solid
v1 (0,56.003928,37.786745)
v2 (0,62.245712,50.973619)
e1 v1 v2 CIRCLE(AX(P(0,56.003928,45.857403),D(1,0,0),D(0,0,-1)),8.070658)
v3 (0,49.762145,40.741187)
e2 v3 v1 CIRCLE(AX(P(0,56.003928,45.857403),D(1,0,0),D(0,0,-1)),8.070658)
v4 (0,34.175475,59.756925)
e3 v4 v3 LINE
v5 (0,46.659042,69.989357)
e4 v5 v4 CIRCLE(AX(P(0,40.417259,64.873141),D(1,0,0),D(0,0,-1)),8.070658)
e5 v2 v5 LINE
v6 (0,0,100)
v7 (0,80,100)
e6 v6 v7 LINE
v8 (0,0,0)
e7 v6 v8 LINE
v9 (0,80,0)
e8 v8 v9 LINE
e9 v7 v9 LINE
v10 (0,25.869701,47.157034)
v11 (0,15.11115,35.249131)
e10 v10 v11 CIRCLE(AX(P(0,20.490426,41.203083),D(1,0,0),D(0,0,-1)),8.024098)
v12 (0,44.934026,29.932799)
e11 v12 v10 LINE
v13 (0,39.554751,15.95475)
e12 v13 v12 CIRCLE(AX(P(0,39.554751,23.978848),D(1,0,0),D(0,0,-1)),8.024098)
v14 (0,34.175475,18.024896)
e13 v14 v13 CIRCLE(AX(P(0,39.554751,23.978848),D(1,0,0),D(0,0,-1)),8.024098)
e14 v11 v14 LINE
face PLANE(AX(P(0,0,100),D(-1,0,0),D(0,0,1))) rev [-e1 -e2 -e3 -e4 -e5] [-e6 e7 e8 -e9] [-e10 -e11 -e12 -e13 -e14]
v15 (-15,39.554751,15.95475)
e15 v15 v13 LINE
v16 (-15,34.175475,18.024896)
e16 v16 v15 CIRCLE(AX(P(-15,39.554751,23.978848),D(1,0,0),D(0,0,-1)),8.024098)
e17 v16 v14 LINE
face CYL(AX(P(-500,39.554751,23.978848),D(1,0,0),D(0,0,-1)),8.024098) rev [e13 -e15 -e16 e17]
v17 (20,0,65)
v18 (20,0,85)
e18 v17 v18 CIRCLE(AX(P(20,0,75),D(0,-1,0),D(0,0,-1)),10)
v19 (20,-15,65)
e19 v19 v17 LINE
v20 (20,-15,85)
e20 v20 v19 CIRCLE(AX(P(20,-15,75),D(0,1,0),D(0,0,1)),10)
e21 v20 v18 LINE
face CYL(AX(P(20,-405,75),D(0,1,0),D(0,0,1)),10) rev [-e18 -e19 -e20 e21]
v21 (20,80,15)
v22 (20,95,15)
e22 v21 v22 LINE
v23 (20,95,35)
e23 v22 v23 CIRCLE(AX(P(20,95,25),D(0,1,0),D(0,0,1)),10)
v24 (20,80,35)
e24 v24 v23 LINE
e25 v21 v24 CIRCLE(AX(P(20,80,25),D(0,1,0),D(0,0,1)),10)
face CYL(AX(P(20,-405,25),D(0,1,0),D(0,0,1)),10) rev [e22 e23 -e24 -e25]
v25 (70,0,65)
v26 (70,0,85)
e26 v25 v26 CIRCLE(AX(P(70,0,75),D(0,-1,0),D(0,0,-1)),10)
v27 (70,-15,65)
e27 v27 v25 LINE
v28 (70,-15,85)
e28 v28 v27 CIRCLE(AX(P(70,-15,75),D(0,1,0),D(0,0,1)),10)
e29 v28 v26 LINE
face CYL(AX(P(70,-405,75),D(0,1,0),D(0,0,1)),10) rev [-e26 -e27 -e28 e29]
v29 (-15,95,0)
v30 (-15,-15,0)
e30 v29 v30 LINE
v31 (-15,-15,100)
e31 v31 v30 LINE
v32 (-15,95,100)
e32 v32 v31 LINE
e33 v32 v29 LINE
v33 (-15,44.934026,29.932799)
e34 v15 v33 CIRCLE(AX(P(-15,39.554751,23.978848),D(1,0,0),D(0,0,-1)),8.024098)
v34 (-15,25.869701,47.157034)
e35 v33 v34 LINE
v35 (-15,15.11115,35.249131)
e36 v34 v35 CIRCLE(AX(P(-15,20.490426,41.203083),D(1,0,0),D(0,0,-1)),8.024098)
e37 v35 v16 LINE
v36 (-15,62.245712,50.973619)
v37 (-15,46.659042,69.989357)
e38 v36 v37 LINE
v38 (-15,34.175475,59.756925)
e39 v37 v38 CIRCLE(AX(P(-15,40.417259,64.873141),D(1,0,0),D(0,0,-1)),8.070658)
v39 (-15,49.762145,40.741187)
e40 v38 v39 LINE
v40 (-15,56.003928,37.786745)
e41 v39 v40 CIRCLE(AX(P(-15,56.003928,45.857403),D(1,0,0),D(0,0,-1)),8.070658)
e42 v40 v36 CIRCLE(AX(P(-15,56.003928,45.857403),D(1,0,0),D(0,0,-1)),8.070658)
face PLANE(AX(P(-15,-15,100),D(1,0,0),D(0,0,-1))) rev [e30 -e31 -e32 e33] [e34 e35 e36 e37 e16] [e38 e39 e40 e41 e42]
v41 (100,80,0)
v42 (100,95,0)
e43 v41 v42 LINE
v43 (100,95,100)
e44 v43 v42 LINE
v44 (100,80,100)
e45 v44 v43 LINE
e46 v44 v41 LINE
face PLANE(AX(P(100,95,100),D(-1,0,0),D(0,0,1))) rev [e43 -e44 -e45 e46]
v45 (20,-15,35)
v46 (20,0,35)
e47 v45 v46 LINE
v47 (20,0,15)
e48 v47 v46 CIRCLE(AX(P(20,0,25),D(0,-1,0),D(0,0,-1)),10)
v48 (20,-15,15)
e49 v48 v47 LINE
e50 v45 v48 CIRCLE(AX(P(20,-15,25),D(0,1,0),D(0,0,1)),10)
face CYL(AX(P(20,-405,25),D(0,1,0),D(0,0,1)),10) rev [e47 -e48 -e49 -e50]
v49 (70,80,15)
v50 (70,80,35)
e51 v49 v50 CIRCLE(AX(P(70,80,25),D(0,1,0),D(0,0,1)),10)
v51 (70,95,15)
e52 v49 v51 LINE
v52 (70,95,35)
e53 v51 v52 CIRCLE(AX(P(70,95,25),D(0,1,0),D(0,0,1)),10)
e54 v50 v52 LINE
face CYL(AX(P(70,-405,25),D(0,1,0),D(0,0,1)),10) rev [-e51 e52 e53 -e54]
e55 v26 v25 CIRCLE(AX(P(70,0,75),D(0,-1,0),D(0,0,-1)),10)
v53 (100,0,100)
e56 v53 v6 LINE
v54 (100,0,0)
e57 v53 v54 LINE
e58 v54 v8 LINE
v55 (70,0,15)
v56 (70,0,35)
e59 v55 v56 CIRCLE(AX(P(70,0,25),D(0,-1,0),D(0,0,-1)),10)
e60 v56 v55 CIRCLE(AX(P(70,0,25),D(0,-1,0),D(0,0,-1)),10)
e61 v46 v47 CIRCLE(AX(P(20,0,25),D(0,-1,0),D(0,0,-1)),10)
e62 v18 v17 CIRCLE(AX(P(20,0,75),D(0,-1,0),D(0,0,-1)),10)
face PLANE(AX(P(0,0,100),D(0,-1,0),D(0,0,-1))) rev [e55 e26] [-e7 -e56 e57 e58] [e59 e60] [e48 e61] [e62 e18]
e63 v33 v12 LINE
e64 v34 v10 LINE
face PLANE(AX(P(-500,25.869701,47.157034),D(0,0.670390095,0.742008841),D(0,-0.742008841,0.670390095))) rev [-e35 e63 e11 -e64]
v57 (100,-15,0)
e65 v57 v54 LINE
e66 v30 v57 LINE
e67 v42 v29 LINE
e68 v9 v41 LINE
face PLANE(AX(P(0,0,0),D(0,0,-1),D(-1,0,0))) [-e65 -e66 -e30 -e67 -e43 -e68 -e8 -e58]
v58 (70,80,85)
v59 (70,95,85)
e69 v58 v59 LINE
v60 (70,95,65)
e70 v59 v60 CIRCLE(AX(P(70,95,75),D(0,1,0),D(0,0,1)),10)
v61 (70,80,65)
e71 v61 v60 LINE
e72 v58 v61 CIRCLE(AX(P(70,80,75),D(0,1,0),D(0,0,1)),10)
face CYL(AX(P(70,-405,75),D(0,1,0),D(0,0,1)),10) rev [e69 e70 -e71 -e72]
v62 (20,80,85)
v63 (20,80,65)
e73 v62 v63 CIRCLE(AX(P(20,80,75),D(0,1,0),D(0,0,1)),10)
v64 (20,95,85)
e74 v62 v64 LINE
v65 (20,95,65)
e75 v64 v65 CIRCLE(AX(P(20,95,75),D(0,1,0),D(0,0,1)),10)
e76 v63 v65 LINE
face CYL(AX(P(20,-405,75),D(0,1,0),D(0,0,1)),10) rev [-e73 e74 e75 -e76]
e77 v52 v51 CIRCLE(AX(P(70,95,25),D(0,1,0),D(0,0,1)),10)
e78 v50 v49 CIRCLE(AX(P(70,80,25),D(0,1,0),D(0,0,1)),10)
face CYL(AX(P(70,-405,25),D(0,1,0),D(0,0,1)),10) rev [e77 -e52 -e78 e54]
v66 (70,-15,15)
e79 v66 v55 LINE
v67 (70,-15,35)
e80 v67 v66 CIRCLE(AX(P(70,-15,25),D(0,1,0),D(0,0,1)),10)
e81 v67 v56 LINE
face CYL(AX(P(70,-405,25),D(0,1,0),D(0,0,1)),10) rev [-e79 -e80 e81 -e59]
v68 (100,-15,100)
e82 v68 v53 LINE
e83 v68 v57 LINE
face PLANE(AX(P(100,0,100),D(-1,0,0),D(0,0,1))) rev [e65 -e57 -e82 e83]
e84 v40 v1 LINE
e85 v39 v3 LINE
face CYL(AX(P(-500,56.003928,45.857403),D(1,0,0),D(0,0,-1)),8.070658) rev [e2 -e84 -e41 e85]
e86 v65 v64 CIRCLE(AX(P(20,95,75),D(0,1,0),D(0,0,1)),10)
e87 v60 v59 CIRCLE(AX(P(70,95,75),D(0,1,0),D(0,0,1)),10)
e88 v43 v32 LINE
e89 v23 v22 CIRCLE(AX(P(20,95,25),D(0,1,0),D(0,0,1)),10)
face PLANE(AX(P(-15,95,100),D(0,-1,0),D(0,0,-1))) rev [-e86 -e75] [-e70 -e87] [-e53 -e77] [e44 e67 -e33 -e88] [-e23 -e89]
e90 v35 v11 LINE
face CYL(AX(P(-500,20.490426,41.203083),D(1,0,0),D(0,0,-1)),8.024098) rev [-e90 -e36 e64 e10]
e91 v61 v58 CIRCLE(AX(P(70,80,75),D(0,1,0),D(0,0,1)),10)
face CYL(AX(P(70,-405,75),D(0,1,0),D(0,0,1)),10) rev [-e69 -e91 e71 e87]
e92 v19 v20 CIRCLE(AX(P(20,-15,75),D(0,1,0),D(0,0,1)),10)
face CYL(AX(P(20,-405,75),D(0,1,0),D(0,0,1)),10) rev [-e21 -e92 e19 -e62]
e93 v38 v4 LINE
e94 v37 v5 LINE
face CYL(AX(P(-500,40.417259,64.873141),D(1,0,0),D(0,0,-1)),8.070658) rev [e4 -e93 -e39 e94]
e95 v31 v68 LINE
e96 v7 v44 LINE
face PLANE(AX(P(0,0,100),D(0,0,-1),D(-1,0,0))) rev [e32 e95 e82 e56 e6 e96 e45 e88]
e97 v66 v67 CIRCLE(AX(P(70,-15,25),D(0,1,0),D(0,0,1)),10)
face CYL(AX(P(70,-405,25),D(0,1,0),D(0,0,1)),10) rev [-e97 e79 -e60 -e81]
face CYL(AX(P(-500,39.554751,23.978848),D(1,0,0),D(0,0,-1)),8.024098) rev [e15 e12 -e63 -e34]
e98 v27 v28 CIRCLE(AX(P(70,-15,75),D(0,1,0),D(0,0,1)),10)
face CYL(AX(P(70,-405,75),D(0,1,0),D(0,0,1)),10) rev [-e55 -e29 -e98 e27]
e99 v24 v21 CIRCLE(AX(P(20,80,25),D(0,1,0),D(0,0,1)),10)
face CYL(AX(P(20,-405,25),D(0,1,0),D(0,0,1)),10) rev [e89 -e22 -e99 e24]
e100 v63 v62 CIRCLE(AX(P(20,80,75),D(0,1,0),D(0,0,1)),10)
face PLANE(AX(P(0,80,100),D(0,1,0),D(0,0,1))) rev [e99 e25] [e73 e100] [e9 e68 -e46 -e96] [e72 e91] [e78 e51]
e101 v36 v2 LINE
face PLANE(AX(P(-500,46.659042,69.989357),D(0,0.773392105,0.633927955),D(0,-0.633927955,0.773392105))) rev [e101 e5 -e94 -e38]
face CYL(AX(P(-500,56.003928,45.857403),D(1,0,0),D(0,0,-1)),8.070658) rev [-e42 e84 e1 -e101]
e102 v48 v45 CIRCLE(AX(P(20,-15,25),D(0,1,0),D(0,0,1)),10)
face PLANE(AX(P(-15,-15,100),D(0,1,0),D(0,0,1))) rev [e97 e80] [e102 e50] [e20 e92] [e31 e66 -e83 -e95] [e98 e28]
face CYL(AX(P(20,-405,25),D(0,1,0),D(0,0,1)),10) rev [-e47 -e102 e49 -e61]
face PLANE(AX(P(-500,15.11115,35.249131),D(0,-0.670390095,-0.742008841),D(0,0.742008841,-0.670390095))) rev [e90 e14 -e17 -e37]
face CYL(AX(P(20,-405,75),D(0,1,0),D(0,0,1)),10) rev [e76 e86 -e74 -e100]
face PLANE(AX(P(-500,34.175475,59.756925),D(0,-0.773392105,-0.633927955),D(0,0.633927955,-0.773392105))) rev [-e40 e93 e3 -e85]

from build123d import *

# Parameters (mm, degrees)
BOSS_EXTRUDE1_DEPTH = 100
SKETCH2_R           = 10
CUT_EXTRUDE1_DEPTH  = 500
CUT_EXTRUDE2_DEPTH  = 500


with BuildPart() as part:
    # Sketch1 → Boss-Extrude1 (new body)
    with BuildSketch(Plane.XY):
        Polygon((0, 0), (100, 0), (100, -15), (-15, -15), (-15, 95), (100, 95), (100, 80), (0, 80), align=None)
    extrude(amount=BOSS_EXTRUDE1_DEPTH)

    # Sketch2 → Cut-Extrude1 (cut)
    with BuildSketch(Plane(origin=(0, 95, 0), x_dir=(1, 0, 0), z_dir=(0, 1, 0))):
        with Locations(Location((20, -25, 0), (0, 0, 270))):
            Circle(SKETCH2_R)
        with Locations(Location((70, -25, 0), (0, 0, 270))):
            Circle(SKETCH2_R)
        with Locations(Location((20, -75, 0), (0, 0, 270))):
            Circle(SKETCH2_R)
        with Locations(Location((70, -75, 0), (0, 0, 270))):
            Circle(SKETCH2_R)
    extrude(amount=-CUT_EXTRUDE1_DEPTH, mode=Mode.SUBTRACT)

    # Sketch3 → Cut-Extrude2 (cut)
    with BuildSketch(Plane(origin=(0, 0, 0), x_dir=(0, 0, -1), z_dir=(1, 0, 0))):
        with BuildLine():
            Line((-69.989356501, 46.65904216), (-50.973619408, 62.245711909))
            ThreePointArc((-50.973619408, 62.245711909), (-39.615619928, 61.120144392), (-40.741187444, 49.762144912))
            Line((-40.741187444, 49.762144912), (-59.756924537, 34.175475163))
            ThreePointArc((-59.756924537, 34.175475163), (-71.114924017, 35.30104268), (-69.989356501, 46.65904216))
        make_face()
        with BuildLine():
            Line((-47.157034179, 25.869701183), (-29.932799149, 44.934026231))
            ThreePointArc((-29.932799149, 44.934026231), (-18.599572272, 45.508702041), (-18.024896462, 34.175475163))
            Line((-18.024896462, 34.175475163), (-35.249131491, 15.111150116))
            ThreePointArc((-35.249131491, 15.111150116), (-46.582358369, 14.536474306), (-47.157034179, 25.869701183))
        make_face()
    extrude(amount=-CUT_EXTRUDE2_DEPTH, mode=Mode.SUBTRACT)


solid = part.part
